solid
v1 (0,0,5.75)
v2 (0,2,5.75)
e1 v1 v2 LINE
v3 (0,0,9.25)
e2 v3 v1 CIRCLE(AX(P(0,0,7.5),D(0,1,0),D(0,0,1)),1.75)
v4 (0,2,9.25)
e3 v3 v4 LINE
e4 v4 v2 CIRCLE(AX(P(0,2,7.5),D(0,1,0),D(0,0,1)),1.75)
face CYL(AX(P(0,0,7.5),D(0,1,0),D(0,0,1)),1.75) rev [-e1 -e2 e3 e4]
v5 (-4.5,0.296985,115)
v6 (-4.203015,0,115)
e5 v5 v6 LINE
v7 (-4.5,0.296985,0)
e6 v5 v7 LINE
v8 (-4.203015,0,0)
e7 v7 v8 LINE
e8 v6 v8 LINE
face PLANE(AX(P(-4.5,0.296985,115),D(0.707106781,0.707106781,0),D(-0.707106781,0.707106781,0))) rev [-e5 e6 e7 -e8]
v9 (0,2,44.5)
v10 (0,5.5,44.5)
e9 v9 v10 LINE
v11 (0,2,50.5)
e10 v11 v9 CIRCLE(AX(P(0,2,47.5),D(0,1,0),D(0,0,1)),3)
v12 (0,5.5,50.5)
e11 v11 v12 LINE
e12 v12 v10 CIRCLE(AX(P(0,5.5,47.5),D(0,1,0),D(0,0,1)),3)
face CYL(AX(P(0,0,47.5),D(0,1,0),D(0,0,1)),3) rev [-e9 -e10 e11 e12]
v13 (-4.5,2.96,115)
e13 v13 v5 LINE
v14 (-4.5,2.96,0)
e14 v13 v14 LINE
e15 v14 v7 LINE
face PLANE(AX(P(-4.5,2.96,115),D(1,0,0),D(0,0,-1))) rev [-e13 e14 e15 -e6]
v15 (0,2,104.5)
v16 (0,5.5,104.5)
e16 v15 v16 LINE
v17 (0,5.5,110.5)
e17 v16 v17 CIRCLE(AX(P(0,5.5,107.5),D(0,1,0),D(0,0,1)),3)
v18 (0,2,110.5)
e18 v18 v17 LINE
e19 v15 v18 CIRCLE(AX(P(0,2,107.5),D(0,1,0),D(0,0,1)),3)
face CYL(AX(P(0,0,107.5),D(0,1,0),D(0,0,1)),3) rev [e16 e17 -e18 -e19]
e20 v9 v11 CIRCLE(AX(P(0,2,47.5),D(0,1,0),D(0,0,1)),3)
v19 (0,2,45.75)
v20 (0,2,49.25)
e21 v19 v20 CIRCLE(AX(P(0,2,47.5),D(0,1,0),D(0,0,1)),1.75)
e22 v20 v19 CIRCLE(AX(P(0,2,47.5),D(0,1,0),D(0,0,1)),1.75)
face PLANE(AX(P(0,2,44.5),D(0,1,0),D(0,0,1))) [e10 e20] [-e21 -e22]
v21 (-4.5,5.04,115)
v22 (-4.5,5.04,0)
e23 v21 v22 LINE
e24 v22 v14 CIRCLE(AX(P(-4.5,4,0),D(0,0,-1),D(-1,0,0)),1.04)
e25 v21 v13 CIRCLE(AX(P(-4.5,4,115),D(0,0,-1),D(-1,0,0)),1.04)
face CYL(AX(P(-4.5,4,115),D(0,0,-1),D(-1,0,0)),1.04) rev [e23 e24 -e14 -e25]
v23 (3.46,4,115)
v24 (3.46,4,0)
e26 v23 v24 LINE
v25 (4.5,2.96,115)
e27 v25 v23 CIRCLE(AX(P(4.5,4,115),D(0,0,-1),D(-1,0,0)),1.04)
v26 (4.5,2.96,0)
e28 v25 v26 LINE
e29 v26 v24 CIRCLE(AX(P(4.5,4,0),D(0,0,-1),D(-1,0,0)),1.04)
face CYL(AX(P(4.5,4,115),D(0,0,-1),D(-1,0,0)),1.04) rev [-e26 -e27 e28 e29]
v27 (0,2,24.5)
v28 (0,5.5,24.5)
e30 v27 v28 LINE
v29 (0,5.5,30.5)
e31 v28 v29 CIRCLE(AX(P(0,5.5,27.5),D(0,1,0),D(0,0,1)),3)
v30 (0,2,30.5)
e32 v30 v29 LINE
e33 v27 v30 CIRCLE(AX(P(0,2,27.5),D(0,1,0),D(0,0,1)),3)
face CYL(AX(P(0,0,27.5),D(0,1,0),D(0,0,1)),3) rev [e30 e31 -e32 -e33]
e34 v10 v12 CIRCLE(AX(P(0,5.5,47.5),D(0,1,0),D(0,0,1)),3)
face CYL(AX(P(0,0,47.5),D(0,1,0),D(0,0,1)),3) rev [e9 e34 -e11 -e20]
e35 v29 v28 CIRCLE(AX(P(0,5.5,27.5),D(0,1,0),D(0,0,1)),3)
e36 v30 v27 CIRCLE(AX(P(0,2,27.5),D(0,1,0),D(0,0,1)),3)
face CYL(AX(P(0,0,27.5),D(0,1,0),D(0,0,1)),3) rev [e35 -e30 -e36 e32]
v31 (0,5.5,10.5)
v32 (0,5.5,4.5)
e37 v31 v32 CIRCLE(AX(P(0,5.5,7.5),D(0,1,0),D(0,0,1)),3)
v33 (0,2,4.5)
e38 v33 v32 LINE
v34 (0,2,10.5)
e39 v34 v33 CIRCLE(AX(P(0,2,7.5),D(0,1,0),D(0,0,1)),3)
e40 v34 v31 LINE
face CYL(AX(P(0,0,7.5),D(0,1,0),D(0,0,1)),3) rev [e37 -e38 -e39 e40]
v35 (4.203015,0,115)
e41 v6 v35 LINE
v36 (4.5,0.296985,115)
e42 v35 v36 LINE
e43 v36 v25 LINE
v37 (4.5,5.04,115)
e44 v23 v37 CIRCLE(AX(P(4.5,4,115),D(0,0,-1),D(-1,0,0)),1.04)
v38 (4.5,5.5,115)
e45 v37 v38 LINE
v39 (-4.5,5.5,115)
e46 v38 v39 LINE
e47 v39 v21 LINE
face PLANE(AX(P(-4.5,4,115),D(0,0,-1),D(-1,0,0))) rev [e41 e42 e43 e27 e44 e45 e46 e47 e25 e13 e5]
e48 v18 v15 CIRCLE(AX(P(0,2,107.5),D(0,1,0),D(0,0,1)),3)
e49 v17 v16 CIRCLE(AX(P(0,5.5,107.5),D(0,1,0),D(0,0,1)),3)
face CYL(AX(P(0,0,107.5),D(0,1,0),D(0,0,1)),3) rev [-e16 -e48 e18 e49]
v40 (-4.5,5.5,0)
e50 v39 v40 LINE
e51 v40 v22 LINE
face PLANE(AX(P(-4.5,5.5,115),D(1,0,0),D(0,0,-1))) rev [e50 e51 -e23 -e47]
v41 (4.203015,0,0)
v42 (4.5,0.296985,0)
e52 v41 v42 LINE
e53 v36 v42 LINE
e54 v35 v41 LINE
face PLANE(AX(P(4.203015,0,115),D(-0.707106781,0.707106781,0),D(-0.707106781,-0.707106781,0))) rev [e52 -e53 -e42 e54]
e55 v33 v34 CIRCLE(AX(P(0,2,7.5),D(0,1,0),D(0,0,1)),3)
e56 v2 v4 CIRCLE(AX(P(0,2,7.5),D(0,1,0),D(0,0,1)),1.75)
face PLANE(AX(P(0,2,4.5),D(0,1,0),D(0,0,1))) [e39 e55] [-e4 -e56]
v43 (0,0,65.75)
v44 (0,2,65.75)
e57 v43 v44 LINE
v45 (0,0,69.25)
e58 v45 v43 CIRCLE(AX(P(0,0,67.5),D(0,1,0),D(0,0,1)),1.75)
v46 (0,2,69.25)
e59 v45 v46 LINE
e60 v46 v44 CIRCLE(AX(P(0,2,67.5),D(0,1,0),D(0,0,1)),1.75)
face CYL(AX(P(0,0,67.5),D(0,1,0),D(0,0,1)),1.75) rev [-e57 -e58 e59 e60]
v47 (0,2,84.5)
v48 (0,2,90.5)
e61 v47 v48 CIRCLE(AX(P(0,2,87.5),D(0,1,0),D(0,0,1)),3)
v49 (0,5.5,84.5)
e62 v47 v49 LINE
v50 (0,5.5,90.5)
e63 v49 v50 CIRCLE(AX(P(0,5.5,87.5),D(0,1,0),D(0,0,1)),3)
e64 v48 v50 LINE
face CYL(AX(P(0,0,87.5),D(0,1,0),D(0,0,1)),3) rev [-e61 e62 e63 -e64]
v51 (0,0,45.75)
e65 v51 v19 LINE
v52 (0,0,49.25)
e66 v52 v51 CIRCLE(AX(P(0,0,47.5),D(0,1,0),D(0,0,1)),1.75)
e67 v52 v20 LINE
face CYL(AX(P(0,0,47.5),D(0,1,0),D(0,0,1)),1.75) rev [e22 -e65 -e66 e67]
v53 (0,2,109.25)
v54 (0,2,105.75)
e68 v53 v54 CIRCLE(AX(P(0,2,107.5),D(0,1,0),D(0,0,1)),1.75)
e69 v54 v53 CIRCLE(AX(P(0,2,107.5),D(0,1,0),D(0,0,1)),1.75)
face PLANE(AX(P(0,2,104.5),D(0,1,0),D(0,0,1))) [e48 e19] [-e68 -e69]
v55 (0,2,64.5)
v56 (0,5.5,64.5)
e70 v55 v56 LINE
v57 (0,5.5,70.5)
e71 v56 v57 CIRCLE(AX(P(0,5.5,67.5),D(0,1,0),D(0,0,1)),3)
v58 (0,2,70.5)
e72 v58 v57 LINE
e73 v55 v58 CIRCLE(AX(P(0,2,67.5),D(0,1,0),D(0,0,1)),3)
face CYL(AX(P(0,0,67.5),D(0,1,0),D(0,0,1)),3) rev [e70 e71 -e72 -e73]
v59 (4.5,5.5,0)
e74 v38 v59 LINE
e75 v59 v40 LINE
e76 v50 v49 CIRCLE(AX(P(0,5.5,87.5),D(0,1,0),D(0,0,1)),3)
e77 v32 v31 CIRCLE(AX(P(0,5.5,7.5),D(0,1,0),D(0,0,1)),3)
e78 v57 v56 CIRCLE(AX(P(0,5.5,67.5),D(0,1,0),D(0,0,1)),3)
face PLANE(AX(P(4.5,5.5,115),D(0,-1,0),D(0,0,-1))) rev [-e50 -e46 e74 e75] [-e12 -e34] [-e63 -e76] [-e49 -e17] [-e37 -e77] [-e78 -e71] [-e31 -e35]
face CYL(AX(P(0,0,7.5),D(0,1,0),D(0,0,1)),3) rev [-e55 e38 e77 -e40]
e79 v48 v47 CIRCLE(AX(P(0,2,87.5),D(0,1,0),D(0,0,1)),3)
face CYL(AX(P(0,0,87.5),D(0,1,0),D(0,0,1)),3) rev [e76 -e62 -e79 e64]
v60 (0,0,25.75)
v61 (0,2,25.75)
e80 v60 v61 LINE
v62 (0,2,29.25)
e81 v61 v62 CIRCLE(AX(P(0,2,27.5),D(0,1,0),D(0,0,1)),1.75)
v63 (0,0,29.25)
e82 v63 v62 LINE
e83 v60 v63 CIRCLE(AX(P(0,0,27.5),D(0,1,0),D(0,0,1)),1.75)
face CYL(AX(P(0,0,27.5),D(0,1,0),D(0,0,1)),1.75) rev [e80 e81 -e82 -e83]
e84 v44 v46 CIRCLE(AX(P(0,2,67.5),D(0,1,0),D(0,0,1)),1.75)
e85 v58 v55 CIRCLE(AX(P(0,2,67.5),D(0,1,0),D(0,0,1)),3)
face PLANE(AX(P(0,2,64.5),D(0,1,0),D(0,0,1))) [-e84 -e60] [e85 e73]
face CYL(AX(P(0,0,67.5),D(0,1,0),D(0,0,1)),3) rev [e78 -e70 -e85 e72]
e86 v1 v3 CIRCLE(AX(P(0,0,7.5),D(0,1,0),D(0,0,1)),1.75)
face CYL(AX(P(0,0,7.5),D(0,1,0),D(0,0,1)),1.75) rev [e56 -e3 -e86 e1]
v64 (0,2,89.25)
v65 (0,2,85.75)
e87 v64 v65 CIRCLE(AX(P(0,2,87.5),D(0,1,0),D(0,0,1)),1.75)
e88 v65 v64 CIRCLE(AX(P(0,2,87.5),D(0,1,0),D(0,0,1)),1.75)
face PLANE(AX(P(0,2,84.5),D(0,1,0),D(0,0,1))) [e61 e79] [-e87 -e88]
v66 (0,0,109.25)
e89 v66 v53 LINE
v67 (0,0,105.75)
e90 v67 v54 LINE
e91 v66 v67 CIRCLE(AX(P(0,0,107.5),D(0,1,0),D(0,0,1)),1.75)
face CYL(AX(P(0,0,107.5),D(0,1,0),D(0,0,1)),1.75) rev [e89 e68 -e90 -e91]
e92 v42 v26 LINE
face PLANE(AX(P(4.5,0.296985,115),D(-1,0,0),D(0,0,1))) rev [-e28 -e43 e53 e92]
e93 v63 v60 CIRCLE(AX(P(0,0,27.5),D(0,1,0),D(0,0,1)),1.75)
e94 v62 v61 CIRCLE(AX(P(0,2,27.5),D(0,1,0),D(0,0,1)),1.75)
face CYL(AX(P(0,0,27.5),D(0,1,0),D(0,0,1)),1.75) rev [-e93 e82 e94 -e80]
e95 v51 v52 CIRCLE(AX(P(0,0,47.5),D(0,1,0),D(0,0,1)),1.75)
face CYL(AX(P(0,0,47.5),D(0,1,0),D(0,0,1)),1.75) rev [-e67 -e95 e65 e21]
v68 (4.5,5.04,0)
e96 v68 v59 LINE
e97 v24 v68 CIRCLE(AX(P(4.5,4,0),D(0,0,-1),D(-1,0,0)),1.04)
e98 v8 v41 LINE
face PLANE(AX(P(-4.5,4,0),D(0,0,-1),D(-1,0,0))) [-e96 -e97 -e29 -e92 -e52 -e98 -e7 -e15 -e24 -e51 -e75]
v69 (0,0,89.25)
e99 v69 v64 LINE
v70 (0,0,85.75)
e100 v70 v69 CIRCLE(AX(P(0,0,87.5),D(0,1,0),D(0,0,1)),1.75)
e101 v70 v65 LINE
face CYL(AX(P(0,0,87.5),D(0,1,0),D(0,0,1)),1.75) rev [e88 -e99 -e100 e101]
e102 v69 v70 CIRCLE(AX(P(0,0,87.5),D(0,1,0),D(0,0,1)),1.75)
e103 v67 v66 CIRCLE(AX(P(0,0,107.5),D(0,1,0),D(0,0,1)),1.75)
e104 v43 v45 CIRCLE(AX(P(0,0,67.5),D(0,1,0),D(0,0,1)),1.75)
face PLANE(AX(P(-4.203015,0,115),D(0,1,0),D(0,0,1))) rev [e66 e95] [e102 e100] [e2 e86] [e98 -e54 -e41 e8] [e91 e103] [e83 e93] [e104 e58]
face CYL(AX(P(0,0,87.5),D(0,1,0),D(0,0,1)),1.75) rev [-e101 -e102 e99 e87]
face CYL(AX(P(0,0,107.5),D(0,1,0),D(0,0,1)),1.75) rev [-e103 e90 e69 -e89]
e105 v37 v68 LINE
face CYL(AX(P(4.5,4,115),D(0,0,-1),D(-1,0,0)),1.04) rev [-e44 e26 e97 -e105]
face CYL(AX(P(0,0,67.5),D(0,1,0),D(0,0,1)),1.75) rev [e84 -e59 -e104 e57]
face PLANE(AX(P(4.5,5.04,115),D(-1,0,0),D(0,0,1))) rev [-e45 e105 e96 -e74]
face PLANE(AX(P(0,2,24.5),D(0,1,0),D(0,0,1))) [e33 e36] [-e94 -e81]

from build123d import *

# Parameters (mm, degrees)
BOSS_EXTRUDE1_DEPTH = 115


with BuildPart() as part:
    # Sketch1 → Boss-Extrude1 (new body)
    with BuildSketch(Plane.XY):
        with BuildLine():
            Line((-4.5, 5.5), (-4.5, 5.04))
            ThreePointArc((-4.5, 5.04), (-3.46, 4), (-4.5, 2.96))
            Line((-4.5, 2.96), (-4.5, 0.296984848))
            Line((-4.5, 0.296984848), (-4.203015152, 0))
            Line((-4.203015152, 0), (4.203015152, 0))
            Line((4.203015152, 0), (4.5, 0.296984848))
            Line((4.5, 0.296984848), (4.5, 2.96))
            ThreePointArc((4.5, 2.96), (3.46, 4), (4.5, 5.04))
            Line((4.5, 5.04), (4.5, 5.5))
            Line((4.5, 5.5), (-4.5, 5.5))
        make_face()
    extrude(amount=BOSS_EXTRUDE1_DEPTH)

    # Sketch2 → Cut-Revolve1 (revolve, cut)
    with BuildSketch(Plane(origin=(0, 0, 0), x_dir=(0, 0, -1), z_dir=(1, 0, 0)), mode=Mode.PRIVATE) as cut_revolve1_sk:
        Polygon((-7.5, 5.5), (-4.5, 5.5), (-4.5, 2), (-5.75, 2), (-5.75, 0), (-7.5, 0), align=None)
    revolve(cut_revolve1_sk.sketch.rotate(Axis((0, 0, 7.5), (0, 1, 0)), 180), axis=Axis((0, 0, 7.5), (0, 1, 0)), mode=Mode.SUBTRACT)

    # Sketch3 → Cut-Revolve2 (revolve, cut)
    with BuildSketch(Plane(origin=(0, 0, 0), x_dir=(0, 0, -1), z_dir=(1, 0, 0)), mode=Mode.PRIVATE) as cut_revolve2_sk:
        Polygon((-107.5, 5.5), (-104.5, 5.5), (-104.5, 2), (-105.75, 2), (-105.75, 0), (-107.5, 0), align=None)
    revolve(cut_revolve2_sk.sketch.rotate(Axis((0, 0, 107.5), (0, 1, 0)), 180), axis=Axis((0, 0, 107.5), (0, 1, 0)), mode=Mode.SUBTRACT)

    # Sketch4 → Cut-Revolve3 (revolve, cut)
    with BuildSketch(Plane(origin=(0, 0, 0), x_dir=(0, 0, -1), z_dir=(1, 0, 0)), mode=Mode.PRIVATE) as cut_revolve3_sk:
        Polygon((-87.5, 5.5), (-84.5, 5.5), (-84.5, 2), (-85.75, 2), (-85.75, 0), (-87.5, 0), align=None)
    revolve(cut_revolve3_sk.sketch.rotate(Axis((0, 0, 87.5), (0, 1, 0)), 180), axis=Axis((0, 0, 87.5), (0, 1, 0)), mode=Mode.SUBTRACT)

    # Sketch5 → Cut-Revolve4 (revolve, cut)
    with BuildSketch(Plane(origin=(0, 0, 0), x_dir=(0, 0, -1), z_dir=(1, 0, 0)), mode=Mode.PRIVATE) as cut_revolve4_sk:
        Polygon((-67.5, 5.5), (-64.5, 5.5), (-64.5, 2), (-65.75, 2), (-65.75, 0), (-67.5, 0), align=None)
    revolve(cut_revolve4_sk.sketch.rotate(Axis((0, 0, 67.5), (0, 1, 0)), 180), axis=Axis((0, 0, 67.5), (0, 1, 0)), mode=Mode.SUBTRACT)

    # Sketch6 → Cut-Revolve5 (revolve, cut)
    with BuildSketch(Plane(origin=(0, 0, 0), x_dir=(0, 0, -1), z_dir=(1, 0, 0)), mode=Mode.PRIVATE) as cut_revolve5_sk:
        Polygon((-47.5, 5.5), (-44.5, 5.5), (-44.5, 2), (-45.75, 2), (-45.75, 0), (-47.5, 0), align=None)
    revolve(cut_revolve5_sk.sketch.rotate(Axis((0, 0, 47.5), (0, 1, 0)), 180), axis=Axis((0, 0, 47.5), (0, 1, 0)), mode=Mode.SUBTRACT)

    # Sketch7 → Cut-Revolve6 (revolve, cut)
    with BuildSketch(Plane(origin=(0, 0, 0), x_dir=(0, 0, -1), z_dir=(1, 0, 0)), mode=Mode.PRIVATE) as cut_revolve6_sk:
        Polygon((-27.5, 5.5), (-24.5, 5.5), (-24.5, 2), (-25.75, 2), (-25.75, 0), (-27.5, 0), align=None)
    revolve(cut_revolve6_sk.sketch.rotate(Axis((0, 0, 27.5), (0, 1, 0)), 180), axis=Axis((0, 0, 27.5), (0, 1, 0)), mode=Mode.SUBTRACT)


solid = part.part
